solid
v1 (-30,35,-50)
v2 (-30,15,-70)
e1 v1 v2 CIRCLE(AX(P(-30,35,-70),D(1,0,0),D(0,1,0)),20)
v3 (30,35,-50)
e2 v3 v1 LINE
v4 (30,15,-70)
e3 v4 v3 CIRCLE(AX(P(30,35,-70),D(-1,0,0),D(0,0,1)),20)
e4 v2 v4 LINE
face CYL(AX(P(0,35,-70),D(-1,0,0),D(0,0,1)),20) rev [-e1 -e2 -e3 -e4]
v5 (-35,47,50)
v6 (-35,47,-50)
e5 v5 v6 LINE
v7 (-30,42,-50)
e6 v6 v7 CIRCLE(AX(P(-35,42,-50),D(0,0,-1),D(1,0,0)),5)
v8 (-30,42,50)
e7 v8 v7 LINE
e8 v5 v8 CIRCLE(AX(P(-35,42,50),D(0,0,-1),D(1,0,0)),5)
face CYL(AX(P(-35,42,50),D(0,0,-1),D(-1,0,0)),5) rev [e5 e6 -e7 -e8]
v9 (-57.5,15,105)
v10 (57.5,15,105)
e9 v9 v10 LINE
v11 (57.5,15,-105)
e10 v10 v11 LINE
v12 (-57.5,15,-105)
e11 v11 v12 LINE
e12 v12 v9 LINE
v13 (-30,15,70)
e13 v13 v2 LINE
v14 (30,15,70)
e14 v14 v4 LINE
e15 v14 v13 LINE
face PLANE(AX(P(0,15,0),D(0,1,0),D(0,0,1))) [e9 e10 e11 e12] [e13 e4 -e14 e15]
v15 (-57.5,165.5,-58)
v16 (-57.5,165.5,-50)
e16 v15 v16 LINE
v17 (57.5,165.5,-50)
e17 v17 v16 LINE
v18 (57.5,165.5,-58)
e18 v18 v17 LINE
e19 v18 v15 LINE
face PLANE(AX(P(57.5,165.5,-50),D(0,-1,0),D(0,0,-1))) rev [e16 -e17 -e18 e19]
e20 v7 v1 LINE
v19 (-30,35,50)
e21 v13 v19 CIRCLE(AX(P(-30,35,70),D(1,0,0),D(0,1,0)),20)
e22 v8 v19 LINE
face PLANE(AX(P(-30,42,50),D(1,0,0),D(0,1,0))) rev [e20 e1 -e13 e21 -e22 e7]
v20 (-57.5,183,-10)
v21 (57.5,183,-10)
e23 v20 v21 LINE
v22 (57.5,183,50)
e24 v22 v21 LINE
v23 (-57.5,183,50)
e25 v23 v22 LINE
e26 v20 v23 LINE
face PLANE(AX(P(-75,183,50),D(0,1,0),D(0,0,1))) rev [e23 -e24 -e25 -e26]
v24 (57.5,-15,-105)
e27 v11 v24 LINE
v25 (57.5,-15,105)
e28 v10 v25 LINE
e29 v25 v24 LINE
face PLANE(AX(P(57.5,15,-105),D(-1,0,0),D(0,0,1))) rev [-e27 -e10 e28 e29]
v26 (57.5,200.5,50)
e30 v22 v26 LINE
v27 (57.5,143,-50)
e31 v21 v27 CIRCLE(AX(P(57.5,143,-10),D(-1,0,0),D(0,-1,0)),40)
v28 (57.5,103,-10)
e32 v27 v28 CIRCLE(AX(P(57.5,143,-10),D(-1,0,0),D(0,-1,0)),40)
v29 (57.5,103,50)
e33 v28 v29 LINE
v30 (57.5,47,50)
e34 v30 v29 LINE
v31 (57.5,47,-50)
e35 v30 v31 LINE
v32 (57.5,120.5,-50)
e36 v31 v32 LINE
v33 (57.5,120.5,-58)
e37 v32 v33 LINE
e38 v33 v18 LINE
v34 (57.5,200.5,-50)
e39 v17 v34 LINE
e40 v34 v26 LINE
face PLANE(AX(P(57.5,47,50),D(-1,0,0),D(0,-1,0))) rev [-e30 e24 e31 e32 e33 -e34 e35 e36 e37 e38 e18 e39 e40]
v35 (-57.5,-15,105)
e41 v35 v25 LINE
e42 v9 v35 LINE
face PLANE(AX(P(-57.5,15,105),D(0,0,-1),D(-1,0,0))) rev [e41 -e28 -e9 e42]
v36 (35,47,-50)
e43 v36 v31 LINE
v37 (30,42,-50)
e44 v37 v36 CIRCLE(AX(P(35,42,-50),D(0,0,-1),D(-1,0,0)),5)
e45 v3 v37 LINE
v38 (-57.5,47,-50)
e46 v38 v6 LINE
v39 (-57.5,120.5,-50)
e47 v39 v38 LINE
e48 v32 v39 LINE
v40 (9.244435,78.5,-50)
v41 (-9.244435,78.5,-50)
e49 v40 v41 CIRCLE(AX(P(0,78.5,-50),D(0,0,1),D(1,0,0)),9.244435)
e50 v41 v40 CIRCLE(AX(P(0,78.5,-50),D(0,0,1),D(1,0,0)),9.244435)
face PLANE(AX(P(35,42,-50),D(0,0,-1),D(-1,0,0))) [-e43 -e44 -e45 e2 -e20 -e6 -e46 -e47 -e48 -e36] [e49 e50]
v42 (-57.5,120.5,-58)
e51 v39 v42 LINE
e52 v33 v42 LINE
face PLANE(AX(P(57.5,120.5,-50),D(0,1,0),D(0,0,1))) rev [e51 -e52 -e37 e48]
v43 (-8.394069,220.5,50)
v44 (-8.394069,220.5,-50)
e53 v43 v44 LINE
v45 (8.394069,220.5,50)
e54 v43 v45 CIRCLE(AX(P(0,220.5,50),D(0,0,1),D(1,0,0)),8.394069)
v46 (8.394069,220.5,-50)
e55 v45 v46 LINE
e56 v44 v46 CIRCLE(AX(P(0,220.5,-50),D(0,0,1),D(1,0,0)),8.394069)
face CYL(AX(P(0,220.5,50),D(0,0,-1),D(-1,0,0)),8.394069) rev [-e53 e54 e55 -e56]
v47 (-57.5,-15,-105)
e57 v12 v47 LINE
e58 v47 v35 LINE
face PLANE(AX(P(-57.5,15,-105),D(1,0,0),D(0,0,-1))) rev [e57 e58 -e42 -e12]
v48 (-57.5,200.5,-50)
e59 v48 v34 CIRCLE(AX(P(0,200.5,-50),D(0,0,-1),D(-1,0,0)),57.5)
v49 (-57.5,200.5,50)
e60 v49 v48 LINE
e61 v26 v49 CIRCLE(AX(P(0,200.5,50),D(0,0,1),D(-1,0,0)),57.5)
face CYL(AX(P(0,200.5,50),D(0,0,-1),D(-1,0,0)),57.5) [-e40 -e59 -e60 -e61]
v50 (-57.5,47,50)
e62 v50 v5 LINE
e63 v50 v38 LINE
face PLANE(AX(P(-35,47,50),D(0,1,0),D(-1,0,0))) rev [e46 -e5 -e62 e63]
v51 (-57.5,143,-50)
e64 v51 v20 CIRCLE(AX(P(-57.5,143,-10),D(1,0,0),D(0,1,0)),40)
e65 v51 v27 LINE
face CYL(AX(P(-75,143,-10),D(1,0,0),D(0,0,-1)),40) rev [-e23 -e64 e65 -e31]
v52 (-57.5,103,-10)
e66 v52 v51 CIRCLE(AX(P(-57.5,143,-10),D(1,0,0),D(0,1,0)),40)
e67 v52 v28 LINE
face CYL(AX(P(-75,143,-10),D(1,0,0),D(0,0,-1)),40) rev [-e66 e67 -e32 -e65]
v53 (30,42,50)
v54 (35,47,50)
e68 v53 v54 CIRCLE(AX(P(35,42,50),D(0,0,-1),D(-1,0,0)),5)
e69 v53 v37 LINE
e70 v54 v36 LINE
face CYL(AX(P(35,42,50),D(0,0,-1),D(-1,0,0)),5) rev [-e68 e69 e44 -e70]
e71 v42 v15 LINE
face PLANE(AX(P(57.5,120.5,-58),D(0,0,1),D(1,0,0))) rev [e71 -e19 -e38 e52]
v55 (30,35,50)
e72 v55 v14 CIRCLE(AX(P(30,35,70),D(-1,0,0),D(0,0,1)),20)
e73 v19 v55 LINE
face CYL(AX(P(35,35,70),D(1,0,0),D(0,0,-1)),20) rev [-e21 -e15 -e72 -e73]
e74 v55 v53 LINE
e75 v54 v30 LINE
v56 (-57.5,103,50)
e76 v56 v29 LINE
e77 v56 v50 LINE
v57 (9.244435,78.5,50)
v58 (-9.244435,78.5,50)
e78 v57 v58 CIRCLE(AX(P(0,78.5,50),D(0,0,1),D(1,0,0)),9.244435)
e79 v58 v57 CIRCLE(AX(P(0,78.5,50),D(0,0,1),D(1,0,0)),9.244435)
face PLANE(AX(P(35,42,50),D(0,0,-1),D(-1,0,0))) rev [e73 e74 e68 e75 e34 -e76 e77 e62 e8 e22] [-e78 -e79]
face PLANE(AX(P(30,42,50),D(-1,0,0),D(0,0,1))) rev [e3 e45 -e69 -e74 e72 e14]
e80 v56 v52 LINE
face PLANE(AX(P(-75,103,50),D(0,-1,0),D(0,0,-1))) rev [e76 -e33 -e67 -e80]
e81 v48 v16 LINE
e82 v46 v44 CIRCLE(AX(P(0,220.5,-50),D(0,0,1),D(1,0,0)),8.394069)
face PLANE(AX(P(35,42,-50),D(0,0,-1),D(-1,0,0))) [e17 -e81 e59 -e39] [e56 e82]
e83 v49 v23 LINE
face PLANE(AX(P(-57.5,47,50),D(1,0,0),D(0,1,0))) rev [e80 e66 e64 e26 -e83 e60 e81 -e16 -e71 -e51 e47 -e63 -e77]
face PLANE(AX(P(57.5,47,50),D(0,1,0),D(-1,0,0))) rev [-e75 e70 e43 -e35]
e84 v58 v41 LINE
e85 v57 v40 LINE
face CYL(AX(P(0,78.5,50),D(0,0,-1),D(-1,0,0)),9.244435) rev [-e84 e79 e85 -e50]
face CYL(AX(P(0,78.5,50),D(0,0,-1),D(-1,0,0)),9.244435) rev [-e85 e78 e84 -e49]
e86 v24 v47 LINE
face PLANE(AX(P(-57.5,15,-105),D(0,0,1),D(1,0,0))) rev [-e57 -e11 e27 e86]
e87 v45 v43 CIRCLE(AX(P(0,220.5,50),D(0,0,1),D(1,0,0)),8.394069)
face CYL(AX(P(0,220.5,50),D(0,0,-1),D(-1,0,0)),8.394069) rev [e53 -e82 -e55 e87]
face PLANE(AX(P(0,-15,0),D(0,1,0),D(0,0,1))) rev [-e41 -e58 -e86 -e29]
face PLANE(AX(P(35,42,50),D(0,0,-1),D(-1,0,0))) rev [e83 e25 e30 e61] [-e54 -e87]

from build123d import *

# Parameters (mm, degrees)
BASE_PLATE_SKETCH_W         = 115
BASE_PLATE_SKETCH_H         = 210
BASE_PLATE_115X210X30_DEPTH = 15
UPRIGHT_PROFILE_SKETCH_R    = 8.394069109
UPRIGHT_PROFILE_SKETCH_R_2  = 9.244434853
UPRIGHT_BODY_DEPTH          = 50
UPRIGHT_ROUND_RADIUS        = 57.5
UPRIGHT_ROUND_LENGTH        = 100
SADDLE_CUT_DEPTH            = 75
SIDE_BOSS_SKETCH_W          = 8
SIDE_BOSS_SKETCH_H          = 45
SIDE_BOSS_DEPTH             = 57.5
EDGE_FILLET_R20_R           = 20


with BuildPart() as part:
    # Base Plate Sketch → Base Plate 115x210x30 (new, symmetric)
    with BuildSketch(Plane(origin=(0, 0, 0), x_dir=(1, 0, 0), z_dir=(0, 1, 0))):
        Rectangle(BASE_PLATE_SKETCH_W, BASE_PLATE_SKETCH_H)
    extrude(amount=BASE_PLATE_115X210X30_DEPTH, both=True)

    # Upright Profile Sketch → Upright Body (add, symmetric)
    with BuildSketch(Plane.XY):
        with BuildLine():
            Line((57.5, 47), (35, 47))
            ThreePointArc((35, 47), (31.464466094, 45.535533906), (30, 42))
            Line((30, 42), (30, 15))
            Line((30, 15), (-30, 15))
            Line((-30, 15), (-30, 42))
            ThreePointArc((-30, 42), (-31.464466094, 45.535533906), (-35, 47))
            Line((-35, 47), (-57.5, 47))
            Line((-57.5, 47), (-57.5, 258))
            Line((-57.5, 258), (57.5, 258))
            Line((57.5, 258), (57.5, 47))
        make_face()
        with Locations((0, 220.5)):
            Circle(UPRIGHT_PROFILE_SKETCH_R, mode=Mode.SUBTRACT)
        with Locations((0, 78.5)):
            Circle(UPRIGHT_PROFILE_SKETCH_R_2, mode=Mode.SUBTRACT)
    extrude(amount=UPRIGHT_BODY_DEPTH, both=True)

    # Upright Round: full round fillet: the end face becomes a half cylinder, R = half its width
    upright_round_face = Plane((0, 258, 0), x_dir=(0, 0, 1), z_dir=(0, 1, 0))  # on the end face: x along it, z out of the body
    upright_round_slab = upright_round_face.offset(-UPRIGHT_ROUND_RADIUS / 2) * Box(UPRIGHT_ROUND_LENGTH, 2 * UPRIGHT_ROUND_RADIUS, UPRIGHT_ROUND_RADIUS, mode=Mode.PRIVATE)  # the body's end, R deep
    upright_round_round = Plane((0, 200.5, 0), x_dir=(0, 1, 0), z_dir=(0, 0, 1)) * Cylinder(UPRIGHT_ROUND_RADIUS, UPRIGHT_ROUND_LENGTH, mode=Mode.PRIVATE)  # its axis R under the face
    add(upright_round_slab - upright_round_round, mode=Mode.SUBTRACT)

    # Saddle Cut Sketch → Saddle Cut (cut, symmetric)
    with BuildSketch(Plane(origin=(0, 0, 0), x_dir=(0, 0, -1), z_dir=(1, 0, 0))):
        with BuildLine():
            Line((-50, 183), (10, 183))
            ThreePointArc((10, 183), (50, 143), (10, 103))
            Line((10, 103), (-50, 103))
            Line((-50, 103), (-50, 183))
        make_face()
    extrude(amount=SADDLE_CUT_DEPTH, both=True, mode=Mode.SUBTRACT)


with BuildPart() as saddle_cut_piece_1:
    # of the separate pieces the step leaves, piece 1, a body of its own (saddle_cut_pieces)
    add(part.part.solids().sort_by_distance((-57.5, -15, -105))[0])



with BuildPart() as saddle_cut_piece_2:
    # of the separate pieces the step leaves, piece 2, a body of its own (saddle_cut_pieces)
    add(part.part.solids().sort_by_distance((-57.5, 200.5, -50))[0])


with BuildPart() as saddle_cut_piece_1_1:
    add(saddle_cut_piece_1.part)

    add(saddle_cut_piece_2.part)  # Side Boss merges Saddle Cut piece 2
    # Side Boss Sketch → Side Boss (add, symmetric)
    with BuildSketch(Plane(origin=(0, 0, 0), x_dir=(0, 0, -1), z_dir=(1, 0, 0))):
        with Locations((54, 143)):
            Rectangle(SIDE_BOSS_SKETCH_W, SIDE_BOSS_SKETCH_H)
    extrude(amount=SIDE_BOSS_DEPTH, both=True)

    # Edge Fillet R20
    edge_fillet_r20_edges = [saddle_cut_piece_1_1.edges().sort_by_distance(p)[0] for p in [
        (0, 15, 50),
        (0, 15, -50),
    ]]
    fillet(edge_fillet_r20_edges, radius=EDGE_FILLET_R20_R)


solid = saddle_cut_piece_1_1.part
